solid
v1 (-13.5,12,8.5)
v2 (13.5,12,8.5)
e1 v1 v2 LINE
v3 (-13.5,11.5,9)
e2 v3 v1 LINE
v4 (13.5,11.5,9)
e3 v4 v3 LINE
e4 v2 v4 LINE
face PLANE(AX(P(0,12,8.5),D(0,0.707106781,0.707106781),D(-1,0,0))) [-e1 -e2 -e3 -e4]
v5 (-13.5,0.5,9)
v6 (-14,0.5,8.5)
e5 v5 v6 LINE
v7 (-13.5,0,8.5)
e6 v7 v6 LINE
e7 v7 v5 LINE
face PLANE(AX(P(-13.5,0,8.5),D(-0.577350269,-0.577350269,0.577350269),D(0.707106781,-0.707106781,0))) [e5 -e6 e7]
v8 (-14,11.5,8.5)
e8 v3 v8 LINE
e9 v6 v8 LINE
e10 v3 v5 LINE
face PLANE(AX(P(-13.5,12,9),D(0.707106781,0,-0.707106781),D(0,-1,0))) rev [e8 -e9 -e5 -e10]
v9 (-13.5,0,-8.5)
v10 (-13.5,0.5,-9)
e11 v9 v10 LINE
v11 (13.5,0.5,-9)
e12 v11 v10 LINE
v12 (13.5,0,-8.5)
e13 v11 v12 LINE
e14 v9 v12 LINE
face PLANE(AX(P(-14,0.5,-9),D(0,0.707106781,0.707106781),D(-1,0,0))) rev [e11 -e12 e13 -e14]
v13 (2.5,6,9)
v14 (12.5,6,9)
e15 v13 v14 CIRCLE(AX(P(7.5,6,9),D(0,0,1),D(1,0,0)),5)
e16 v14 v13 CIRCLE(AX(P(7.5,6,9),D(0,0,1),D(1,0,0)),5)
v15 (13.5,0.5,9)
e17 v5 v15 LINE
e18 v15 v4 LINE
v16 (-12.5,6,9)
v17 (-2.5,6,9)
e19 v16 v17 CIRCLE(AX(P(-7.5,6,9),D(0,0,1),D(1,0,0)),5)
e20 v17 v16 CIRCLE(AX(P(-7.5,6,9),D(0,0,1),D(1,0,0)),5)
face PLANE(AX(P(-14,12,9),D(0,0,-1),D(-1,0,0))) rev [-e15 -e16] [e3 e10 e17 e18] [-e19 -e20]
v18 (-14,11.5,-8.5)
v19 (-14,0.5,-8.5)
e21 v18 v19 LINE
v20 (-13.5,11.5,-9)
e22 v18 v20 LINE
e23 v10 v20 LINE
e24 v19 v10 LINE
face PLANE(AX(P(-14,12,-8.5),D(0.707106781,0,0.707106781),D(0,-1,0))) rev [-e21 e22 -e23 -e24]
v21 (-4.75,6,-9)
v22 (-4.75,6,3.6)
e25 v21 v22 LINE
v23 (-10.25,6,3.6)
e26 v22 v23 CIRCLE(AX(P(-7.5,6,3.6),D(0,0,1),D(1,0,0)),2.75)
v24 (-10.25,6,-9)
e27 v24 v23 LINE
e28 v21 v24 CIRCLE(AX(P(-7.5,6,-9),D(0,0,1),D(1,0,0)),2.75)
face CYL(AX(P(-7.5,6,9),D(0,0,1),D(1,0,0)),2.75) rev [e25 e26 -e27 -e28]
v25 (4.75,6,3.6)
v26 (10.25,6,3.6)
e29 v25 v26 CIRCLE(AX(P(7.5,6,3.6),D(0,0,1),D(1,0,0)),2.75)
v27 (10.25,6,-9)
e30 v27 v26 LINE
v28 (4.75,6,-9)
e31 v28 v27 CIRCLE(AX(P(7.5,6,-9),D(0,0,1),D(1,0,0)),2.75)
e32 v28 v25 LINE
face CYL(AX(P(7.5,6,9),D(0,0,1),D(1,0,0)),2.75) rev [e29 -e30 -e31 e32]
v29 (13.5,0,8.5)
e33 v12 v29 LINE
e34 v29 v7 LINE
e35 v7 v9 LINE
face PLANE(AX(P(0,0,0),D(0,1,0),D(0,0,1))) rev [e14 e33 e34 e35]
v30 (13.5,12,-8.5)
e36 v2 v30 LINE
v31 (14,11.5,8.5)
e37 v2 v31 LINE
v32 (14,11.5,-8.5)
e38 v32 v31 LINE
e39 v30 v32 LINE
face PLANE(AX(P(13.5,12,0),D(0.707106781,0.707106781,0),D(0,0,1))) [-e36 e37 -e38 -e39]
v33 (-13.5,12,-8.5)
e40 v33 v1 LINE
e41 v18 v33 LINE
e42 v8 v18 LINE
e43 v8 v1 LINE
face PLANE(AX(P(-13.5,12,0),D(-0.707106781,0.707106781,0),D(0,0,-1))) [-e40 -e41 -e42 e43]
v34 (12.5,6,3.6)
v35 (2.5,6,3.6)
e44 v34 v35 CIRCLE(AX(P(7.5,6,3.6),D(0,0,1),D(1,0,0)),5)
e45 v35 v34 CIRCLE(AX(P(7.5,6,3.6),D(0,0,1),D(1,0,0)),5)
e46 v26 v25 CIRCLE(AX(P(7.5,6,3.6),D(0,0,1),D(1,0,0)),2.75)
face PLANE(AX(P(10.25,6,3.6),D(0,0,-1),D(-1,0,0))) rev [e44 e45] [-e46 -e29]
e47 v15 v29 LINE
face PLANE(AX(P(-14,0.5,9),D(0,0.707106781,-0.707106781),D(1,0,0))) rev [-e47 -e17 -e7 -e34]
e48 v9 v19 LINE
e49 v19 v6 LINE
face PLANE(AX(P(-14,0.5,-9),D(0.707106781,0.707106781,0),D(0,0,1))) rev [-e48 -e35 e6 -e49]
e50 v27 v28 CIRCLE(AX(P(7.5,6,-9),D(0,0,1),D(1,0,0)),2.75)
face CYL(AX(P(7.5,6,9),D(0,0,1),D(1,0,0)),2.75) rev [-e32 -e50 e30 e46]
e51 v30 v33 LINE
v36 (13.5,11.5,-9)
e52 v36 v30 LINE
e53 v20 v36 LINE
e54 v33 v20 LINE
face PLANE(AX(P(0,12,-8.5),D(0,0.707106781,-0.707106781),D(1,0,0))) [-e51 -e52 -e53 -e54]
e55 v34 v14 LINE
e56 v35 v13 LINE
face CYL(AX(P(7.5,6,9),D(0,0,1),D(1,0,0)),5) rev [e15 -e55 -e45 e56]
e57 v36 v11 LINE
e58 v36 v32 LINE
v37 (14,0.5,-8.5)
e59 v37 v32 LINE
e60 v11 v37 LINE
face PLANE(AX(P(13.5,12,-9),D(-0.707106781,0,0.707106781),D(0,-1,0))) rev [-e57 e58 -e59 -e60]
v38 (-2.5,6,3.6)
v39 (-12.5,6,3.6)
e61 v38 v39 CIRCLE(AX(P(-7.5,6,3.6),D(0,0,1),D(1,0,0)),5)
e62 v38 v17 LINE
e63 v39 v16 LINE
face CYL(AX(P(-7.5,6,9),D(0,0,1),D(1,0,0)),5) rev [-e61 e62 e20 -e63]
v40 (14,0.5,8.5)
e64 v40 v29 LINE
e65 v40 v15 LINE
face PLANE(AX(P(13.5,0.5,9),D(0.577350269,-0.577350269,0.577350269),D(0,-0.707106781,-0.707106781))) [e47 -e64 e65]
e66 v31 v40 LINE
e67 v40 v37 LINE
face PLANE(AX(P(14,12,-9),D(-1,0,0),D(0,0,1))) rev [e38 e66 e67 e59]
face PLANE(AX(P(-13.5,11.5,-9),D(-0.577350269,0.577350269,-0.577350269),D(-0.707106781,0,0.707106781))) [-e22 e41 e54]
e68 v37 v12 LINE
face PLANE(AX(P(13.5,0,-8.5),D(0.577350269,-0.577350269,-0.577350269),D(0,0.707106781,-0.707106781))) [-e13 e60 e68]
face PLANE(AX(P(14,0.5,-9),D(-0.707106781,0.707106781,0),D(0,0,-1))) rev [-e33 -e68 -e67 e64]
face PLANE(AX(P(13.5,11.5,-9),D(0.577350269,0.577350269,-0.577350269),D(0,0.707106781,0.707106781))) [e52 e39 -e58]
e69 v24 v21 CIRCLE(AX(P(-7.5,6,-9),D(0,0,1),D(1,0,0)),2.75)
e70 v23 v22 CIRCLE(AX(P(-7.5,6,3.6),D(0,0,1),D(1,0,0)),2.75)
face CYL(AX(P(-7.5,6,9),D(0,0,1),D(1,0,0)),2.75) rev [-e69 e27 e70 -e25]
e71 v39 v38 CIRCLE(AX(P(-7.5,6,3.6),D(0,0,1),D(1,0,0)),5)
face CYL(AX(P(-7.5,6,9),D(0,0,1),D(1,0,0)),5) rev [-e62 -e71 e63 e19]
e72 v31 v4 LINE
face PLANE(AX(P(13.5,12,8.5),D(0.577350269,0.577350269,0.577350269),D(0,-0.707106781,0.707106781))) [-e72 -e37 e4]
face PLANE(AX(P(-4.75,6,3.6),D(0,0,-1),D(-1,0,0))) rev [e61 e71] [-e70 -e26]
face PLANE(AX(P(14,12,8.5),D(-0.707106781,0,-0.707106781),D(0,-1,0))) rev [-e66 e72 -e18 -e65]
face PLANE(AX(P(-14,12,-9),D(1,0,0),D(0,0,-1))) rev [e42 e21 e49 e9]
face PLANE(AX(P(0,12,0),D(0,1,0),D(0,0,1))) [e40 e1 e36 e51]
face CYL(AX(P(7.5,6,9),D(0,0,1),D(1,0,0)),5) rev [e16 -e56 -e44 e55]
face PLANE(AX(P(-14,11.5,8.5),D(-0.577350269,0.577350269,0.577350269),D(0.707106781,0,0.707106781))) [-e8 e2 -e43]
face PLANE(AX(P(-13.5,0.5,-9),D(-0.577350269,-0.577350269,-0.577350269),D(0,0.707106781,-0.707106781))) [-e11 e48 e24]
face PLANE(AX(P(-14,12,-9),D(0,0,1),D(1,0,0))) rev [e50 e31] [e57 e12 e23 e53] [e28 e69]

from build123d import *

# Parameters (mm, degrees)
SKETCH_1_W                   = 28
SKETCH_1_H                   = 18
EXTRUDE_1_DEPTH              = 12
HOLE_WIZARD_M5_1_D           = 5.5
HOLE_WIZARD_M5_1_CBORE_D     = 10
HOLE_WIZARD_M5_1_CBORE_DEPTH = 5.4
CHAMFER_1_SIZE               = 0.5


with BuildPart() as part:
    # 草图1 → 凸台-拉伸1 (new body)
    with BuildSketch(Plane(origin=(0, 0, 0), x_dir=(1, 0, 0), z_dir=(0, 1, 0))):
        Rectangle(SKETCH_1_W, SKETCH_1_H)
    extrude(amount=EXTRUDE_1_DEPTH)

    # M5 六角凹头螺钉的柱形沉头孔1 (through all)
    with Locations(Plane.XY.offset(9)):
        with Locations((-7.5, 6), (7.5, 6)):
            CounterBoreHole(HOLE_WIZARD_M5_1_D / 2, HOLE_WIZARD_M5_1_CBORE_D / 2, HOLE_WIZARD_M5_1_CBORE_DEPTH)

    # 倒角1
    chamfer_1_edges = [part.edges().sort_by_distance(p)[0] for p in [
        (-14, 12, 0),
        (0, 12, 9),
        (14, 12, 0),
        (0, 0, 9),
        (-14, 0, 0),
        (0, 0, -9),
        (14, 0, 0),
        (0, 12, -9),
        (14, 6, 9),
        (-14, 6, 9),
        (-14, 6, -9),
        (14, 6, -9),
    ]]
    chamfer(chamfer_1_edges, length=CHAMFER_1_SIZE)


solid = part.part
